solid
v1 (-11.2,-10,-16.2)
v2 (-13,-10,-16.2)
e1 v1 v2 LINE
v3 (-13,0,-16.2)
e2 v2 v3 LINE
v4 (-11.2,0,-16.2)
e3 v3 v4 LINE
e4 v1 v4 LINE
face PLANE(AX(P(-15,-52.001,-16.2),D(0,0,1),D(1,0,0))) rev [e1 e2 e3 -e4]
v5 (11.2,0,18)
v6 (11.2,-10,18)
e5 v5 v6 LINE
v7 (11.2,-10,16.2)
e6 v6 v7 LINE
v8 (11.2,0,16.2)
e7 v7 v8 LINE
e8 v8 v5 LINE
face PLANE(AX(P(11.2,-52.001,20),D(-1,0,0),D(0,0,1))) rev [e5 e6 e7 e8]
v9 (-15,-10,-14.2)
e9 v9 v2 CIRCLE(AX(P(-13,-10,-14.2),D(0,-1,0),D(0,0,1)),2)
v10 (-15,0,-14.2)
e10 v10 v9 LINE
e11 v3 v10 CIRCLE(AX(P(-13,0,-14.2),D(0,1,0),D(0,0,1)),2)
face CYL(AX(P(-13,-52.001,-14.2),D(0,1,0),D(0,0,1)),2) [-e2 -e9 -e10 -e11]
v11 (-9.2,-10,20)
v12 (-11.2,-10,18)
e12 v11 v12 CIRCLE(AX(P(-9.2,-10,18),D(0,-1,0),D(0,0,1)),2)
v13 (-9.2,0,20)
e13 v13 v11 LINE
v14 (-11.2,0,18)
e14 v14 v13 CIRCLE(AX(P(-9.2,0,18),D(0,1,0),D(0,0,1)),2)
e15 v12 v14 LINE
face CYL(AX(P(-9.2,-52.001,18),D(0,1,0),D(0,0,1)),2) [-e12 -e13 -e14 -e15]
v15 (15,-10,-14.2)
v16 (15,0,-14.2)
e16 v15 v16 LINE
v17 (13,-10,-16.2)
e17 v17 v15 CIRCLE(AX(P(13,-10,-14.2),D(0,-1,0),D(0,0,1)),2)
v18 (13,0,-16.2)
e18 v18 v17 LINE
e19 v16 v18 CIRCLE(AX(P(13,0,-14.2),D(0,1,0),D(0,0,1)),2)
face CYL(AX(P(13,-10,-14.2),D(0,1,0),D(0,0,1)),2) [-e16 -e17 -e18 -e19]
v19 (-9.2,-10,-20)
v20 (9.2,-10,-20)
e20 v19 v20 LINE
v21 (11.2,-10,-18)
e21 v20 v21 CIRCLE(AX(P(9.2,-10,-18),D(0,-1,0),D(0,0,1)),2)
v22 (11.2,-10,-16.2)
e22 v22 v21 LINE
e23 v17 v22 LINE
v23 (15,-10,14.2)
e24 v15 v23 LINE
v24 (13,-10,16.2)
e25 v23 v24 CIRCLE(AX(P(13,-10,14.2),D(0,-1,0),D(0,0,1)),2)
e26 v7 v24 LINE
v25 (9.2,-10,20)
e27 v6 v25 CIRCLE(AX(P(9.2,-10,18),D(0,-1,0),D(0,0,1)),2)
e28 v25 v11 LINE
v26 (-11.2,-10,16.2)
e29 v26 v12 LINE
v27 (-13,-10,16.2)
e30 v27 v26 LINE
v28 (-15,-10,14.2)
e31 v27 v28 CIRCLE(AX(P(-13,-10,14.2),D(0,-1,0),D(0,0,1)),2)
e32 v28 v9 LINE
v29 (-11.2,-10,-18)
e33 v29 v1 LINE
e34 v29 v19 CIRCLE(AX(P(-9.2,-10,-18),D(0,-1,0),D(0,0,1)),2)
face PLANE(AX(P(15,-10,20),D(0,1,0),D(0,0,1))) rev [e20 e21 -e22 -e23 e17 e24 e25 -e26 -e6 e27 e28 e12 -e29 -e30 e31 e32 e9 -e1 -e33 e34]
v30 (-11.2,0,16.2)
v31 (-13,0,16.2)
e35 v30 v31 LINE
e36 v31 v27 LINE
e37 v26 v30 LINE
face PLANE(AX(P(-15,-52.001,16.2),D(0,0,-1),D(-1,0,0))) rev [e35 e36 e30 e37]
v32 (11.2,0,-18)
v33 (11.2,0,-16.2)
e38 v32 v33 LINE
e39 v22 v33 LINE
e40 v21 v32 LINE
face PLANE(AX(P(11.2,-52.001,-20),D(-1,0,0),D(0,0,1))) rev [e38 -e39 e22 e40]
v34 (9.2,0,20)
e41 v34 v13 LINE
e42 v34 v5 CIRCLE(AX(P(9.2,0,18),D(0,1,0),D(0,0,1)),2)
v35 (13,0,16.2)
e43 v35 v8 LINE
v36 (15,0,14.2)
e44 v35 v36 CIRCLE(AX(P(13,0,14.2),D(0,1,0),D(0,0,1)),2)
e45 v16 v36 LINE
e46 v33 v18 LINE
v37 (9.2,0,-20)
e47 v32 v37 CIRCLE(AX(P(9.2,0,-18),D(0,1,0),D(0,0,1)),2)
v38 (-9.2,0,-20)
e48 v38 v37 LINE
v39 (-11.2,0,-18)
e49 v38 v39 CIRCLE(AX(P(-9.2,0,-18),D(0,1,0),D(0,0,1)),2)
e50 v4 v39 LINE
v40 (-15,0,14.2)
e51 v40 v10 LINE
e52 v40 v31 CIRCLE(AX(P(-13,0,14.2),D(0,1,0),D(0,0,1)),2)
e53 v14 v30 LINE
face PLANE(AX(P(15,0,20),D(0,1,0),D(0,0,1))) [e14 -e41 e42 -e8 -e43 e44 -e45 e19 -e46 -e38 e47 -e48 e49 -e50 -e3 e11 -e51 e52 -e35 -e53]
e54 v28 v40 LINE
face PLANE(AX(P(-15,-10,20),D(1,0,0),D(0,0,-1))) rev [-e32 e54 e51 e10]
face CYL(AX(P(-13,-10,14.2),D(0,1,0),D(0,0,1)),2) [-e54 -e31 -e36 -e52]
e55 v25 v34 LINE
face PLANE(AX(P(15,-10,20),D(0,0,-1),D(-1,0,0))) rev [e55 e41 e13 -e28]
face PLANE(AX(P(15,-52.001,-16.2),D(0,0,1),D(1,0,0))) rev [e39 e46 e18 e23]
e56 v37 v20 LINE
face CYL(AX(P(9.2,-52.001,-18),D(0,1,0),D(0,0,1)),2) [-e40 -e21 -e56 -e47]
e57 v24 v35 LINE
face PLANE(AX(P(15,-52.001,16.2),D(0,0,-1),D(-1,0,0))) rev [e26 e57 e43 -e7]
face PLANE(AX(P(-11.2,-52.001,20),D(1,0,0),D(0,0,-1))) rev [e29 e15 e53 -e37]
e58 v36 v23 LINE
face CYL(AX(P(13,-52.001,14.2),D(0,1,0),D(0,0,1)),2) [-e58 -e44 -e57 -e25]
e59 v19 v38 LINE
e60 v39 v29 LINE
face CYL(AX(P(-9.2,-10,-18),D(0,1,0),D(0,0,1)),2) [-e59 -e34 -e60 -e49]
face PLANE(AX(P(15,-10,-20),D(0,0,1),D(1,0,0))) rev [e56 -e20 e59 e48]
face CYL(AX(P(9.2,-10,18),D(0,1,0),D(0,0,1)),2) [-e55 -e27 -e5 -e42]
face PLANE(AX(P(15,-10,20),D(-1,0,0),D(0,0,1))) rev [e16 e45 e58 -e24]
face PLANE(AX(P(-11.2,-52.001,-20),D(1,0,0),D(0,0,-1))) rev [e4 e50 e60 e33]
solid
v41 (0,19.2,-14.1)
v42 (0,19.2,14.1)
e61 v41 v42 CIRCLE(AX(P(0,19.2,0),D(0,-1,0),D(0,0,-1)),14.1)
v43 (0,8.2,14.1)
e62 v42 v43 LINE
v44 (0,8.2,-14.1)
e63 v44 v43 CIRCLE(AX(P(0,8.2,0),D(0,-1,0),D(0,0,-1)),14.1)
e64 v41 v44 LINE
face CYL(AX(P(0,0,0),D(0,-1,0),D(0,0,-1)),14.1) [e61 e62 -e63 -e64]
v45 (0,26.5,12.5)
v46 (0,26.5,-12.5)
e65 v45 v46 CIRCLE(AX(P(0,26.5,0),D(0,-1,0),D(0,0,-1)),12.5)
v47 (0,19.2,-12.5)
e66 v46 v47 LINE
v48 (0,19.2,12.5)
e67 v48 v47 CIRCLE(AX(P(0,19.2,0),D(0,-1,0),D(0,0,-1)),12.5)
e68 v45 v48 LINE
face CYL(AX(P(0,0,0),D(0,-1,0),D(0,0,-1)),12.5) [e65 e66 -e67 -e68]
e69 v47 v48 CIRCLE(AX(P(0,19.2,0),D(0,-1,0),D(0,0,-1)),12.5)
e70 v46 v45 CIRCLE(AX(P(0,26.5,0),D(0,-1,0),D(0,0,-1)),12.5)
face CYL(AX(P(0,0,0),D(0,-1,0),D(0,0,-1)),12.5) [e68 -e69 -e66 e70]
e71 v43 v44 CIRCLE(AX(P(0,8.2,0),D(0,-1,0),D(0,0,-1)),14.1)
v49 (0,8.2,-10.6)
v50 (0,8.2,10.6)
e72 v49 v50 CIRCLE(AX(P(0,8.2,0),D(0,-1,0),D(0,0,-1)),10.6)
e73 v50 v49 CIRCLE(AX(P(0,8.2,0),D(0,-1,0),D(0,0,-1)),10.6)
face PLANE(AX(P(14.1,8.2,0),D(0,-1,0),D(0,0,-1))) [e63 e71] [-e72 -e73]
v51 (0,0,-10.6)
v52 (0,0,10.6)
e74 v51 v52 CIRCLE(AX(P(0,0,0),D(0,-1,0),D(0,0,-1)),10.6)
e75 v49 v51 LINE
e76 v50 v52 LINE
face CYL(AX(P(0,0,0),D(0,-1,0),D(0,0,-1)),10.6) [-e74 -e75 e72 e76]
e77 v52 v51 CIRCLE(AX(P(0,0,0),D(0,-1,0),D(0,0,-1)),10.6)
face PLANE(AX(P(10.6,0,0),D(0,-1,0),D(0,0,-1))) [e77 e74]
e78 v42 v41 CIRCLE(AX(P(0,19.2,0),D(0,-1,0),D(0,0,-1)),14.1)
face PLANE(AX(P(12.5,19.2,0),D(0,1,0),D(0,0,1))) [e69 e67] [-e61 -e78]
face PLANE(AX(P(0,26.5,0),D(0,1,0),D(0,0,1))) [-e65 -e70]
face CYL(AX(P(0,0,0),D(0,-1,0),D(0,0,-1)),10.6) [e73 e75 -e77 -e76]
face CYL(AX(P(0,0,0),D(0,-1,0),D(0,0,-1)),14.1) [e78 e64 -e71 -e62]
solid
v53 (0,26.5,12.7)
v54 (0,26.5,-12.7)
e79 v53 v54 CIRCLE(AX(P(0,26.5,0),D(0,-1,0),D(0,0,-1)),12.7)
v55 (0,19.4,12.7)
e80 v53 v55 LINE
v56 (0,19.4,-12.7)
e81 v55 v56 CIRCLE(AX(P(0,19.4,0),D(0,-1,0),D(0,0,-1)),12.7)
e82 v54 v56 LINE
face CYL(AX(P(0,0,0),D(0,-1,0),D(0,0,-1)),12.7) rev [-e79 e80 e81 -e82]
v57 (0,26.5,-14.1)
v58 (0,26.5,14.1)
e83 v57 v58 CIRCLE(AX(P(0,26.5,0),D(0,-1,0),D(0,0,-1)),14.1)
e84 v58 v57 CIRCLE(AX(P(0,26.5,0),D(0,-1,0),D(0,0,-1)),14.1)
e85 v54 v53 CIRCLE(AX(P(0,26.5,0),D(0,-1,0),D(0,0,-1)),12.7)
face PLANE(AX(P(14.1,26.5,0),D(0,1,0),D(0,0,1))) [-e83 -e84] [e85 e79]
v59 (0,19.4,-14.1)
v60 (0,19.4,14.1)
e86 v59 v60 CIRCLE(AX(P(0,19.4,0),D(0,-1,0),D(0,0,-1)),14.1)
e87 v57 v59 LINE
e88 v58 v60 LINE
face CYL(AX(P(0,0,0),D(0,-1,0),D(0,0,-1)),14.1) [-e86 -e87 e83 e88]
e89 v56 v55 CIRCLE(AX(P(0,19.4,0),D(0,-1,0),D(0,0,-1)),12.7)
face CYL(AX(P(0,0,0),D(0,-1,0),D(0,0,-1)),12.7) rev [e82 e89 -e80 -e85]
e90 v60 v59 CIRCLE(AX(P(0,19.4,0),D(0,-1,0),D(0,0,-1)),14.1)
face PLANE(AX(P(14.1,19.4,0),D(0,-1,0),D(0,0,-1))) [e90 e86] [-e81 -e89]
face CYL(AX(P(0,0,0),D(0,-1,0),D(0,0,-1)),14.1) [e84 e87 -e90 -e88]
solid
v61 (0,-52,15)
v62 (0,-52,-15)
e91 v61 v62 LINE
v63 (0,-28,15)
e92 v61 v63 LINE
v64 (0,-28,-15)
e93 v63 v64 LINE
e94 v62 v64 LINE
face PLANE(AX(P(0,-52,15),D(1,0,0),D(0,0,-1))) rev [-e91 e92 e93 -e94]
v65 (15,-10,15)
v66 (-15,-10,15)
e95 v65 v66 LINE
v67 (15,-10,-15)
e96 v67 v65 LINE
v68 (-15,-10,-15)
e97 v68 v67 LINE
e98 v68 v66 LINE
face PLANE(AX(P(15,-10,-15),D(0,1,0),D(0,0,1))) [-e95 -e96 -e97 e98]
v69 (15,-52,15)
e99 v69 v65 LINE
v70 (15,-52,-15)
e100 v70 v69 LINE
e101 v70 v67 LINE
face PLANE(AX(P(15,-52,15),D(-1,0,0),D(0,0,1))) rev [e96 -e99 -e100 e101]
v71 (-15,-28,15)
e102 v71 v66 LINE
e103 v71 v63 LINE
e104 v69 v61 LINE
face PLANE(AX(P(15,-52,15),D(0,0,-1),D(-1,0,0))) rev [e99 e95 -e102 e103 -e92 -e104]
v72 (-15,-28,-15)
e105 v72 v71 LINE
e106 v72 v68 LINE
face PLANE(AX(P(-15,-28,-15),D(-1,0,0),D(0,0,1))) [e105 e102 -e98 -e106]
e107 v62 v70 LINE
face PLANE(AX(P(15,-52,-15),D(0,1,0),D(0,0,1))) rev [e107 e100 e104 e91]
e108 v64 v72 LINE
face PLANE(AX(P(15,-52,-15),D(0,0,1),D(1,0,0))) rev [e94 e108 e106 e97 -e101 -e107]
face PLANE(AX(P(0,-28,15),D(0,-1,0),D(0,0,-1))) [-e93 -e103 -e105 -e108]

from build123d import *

# Parameters (mm, degrees)
SKETCH_2_W          = 30
SKETCH_2_H          = 40
EXTRUDE_1_DEPTH     = 10
SKETCH_3_W          = 15
SKETCH_3_H          = 30
EXTRUDE_2_DEPTH     = 42
SKETCH_7_W          = 3.8
SKETCH_7_H          = 3.8
CUT_EXTRUDE_2_DEPTH = 10
FILLET_1_R          = 2
SKETCH_8_W          = 15
SKETCH_8_H          = 30
EXTRUDE_3_DEPTH     = 18
SKETCH_11_W         = 1.4
SKETCH_11_H         = 7.1


with BuildPart() as part:
    # 草图1 → 旋转1 (revolve)
    with BuildSketch(Plane.XY, mode=Mode.PRIVATE) as revolve_1_sk:
        Polygon((12.5, 19.2), (14.1, 19.2), (14.1, 8.2), (10.6, 8.2), (10.6, 0), (0, 0), (0, 19.2), (0, 26.5), (12.5, 26.5), align=None)
    revolve(revolve_1_sk.sketch.rotate(Axis((0, 0, 0), (0, 1, 0)), 90), axis=Axis((0, 0, 0), (0, 1, 0)))


with BuildPart() as body_2:
    # 草图2 → 拉伸1 (new body)
    with BuildSketch(Plane.XZ):
        Rectangle(SKETCH_2_W, SKETCH_2_H)
    extrude(amount=EXTRUDE_1_DEPTH)

    # 草图7 → 切除-拉伸2 (cut)
    with BuildSketch(Plane(origin=(0, 0, 0), x_dir=(-1, 0, 0), z_dir=(0, 1, 0))):
        with Locations((-13.1, 18.1)):
            Rectangle(SKETCH_7_W, SKETCH_7_H)
        with Locations((13.1, 18.1)):
            Rectangle(SKETCH_7_W, SKETCH_7_H)
        with Locations((13.1, -18.1)):
            Rectangle(SKETCH_7_W, SKETCH_7_H)
        with Locations((-13.1, -18.1)):
            Rectangle(SKETCH_7_W, SKETCH_7_H)
    extrude(amount=-CUT_EXTRUDE_2_DEPTH, mode=Mode.SUBTRACT)

    # 圆角1
    fillet_1_edges = [body_2.edges().sort_by_distance(p)[0] for p in [
        (15, -5, 16.2),
        (11.2, -5, 20),
        (-11.2, -5, 20),
        (-15, -5, 16.2),
        (-15, -5, -16.2),
        (-11.2, -5, -20),
        (11.2, -5, -20),
        (15, -5, -16.2),
    ]]
    fillet(fillet_1_edges, radius=FILLET_1_R)


with BuildPart() as body_3:
    # 草图3 → 拉伸2 (new body)
    with BuildSketch(Plane.XZ.offset(10)):
        with Locations((7.5, 0)):
            Rectangle(SKETCH_3_W, SKETCH_3_H)
    extrude(amount=EXTRUDE_2_DEPTH)

    # 草图8 → 拉伸3 (add)
    with BuildSketch(Plane(origin=(0, -10, 0), x_dir=(-1, 0, 0), z_dir=(0, 1, 0))):
        with Locations((7.5, 0)):
            Rectangle(SKETCH_8_W, SKETCH_8_H)
    extrude(amount=-EXTRUDE_3_DEPTH)


with BuildPart() as body_4:
    # 草图11 → 旋转2 (revolve)
    with BuildSketch(Plane.XY, mode=Mode.PRIVATE) as revolve_2_sk:
        with Locations((13.4, 22.95)):
            Rectangle(SKETCH_11_W, SKETCH_11_H)
    revolve(revolve_2_sk.sketch.rotate(Axis((0, 0, 0), (0, 1, 0)), 90), axis=Axis((0, 0, 0), (0, 1, 0)))


solid = Compound([part.part, body_2.part, body_3.part, body_4.part])
